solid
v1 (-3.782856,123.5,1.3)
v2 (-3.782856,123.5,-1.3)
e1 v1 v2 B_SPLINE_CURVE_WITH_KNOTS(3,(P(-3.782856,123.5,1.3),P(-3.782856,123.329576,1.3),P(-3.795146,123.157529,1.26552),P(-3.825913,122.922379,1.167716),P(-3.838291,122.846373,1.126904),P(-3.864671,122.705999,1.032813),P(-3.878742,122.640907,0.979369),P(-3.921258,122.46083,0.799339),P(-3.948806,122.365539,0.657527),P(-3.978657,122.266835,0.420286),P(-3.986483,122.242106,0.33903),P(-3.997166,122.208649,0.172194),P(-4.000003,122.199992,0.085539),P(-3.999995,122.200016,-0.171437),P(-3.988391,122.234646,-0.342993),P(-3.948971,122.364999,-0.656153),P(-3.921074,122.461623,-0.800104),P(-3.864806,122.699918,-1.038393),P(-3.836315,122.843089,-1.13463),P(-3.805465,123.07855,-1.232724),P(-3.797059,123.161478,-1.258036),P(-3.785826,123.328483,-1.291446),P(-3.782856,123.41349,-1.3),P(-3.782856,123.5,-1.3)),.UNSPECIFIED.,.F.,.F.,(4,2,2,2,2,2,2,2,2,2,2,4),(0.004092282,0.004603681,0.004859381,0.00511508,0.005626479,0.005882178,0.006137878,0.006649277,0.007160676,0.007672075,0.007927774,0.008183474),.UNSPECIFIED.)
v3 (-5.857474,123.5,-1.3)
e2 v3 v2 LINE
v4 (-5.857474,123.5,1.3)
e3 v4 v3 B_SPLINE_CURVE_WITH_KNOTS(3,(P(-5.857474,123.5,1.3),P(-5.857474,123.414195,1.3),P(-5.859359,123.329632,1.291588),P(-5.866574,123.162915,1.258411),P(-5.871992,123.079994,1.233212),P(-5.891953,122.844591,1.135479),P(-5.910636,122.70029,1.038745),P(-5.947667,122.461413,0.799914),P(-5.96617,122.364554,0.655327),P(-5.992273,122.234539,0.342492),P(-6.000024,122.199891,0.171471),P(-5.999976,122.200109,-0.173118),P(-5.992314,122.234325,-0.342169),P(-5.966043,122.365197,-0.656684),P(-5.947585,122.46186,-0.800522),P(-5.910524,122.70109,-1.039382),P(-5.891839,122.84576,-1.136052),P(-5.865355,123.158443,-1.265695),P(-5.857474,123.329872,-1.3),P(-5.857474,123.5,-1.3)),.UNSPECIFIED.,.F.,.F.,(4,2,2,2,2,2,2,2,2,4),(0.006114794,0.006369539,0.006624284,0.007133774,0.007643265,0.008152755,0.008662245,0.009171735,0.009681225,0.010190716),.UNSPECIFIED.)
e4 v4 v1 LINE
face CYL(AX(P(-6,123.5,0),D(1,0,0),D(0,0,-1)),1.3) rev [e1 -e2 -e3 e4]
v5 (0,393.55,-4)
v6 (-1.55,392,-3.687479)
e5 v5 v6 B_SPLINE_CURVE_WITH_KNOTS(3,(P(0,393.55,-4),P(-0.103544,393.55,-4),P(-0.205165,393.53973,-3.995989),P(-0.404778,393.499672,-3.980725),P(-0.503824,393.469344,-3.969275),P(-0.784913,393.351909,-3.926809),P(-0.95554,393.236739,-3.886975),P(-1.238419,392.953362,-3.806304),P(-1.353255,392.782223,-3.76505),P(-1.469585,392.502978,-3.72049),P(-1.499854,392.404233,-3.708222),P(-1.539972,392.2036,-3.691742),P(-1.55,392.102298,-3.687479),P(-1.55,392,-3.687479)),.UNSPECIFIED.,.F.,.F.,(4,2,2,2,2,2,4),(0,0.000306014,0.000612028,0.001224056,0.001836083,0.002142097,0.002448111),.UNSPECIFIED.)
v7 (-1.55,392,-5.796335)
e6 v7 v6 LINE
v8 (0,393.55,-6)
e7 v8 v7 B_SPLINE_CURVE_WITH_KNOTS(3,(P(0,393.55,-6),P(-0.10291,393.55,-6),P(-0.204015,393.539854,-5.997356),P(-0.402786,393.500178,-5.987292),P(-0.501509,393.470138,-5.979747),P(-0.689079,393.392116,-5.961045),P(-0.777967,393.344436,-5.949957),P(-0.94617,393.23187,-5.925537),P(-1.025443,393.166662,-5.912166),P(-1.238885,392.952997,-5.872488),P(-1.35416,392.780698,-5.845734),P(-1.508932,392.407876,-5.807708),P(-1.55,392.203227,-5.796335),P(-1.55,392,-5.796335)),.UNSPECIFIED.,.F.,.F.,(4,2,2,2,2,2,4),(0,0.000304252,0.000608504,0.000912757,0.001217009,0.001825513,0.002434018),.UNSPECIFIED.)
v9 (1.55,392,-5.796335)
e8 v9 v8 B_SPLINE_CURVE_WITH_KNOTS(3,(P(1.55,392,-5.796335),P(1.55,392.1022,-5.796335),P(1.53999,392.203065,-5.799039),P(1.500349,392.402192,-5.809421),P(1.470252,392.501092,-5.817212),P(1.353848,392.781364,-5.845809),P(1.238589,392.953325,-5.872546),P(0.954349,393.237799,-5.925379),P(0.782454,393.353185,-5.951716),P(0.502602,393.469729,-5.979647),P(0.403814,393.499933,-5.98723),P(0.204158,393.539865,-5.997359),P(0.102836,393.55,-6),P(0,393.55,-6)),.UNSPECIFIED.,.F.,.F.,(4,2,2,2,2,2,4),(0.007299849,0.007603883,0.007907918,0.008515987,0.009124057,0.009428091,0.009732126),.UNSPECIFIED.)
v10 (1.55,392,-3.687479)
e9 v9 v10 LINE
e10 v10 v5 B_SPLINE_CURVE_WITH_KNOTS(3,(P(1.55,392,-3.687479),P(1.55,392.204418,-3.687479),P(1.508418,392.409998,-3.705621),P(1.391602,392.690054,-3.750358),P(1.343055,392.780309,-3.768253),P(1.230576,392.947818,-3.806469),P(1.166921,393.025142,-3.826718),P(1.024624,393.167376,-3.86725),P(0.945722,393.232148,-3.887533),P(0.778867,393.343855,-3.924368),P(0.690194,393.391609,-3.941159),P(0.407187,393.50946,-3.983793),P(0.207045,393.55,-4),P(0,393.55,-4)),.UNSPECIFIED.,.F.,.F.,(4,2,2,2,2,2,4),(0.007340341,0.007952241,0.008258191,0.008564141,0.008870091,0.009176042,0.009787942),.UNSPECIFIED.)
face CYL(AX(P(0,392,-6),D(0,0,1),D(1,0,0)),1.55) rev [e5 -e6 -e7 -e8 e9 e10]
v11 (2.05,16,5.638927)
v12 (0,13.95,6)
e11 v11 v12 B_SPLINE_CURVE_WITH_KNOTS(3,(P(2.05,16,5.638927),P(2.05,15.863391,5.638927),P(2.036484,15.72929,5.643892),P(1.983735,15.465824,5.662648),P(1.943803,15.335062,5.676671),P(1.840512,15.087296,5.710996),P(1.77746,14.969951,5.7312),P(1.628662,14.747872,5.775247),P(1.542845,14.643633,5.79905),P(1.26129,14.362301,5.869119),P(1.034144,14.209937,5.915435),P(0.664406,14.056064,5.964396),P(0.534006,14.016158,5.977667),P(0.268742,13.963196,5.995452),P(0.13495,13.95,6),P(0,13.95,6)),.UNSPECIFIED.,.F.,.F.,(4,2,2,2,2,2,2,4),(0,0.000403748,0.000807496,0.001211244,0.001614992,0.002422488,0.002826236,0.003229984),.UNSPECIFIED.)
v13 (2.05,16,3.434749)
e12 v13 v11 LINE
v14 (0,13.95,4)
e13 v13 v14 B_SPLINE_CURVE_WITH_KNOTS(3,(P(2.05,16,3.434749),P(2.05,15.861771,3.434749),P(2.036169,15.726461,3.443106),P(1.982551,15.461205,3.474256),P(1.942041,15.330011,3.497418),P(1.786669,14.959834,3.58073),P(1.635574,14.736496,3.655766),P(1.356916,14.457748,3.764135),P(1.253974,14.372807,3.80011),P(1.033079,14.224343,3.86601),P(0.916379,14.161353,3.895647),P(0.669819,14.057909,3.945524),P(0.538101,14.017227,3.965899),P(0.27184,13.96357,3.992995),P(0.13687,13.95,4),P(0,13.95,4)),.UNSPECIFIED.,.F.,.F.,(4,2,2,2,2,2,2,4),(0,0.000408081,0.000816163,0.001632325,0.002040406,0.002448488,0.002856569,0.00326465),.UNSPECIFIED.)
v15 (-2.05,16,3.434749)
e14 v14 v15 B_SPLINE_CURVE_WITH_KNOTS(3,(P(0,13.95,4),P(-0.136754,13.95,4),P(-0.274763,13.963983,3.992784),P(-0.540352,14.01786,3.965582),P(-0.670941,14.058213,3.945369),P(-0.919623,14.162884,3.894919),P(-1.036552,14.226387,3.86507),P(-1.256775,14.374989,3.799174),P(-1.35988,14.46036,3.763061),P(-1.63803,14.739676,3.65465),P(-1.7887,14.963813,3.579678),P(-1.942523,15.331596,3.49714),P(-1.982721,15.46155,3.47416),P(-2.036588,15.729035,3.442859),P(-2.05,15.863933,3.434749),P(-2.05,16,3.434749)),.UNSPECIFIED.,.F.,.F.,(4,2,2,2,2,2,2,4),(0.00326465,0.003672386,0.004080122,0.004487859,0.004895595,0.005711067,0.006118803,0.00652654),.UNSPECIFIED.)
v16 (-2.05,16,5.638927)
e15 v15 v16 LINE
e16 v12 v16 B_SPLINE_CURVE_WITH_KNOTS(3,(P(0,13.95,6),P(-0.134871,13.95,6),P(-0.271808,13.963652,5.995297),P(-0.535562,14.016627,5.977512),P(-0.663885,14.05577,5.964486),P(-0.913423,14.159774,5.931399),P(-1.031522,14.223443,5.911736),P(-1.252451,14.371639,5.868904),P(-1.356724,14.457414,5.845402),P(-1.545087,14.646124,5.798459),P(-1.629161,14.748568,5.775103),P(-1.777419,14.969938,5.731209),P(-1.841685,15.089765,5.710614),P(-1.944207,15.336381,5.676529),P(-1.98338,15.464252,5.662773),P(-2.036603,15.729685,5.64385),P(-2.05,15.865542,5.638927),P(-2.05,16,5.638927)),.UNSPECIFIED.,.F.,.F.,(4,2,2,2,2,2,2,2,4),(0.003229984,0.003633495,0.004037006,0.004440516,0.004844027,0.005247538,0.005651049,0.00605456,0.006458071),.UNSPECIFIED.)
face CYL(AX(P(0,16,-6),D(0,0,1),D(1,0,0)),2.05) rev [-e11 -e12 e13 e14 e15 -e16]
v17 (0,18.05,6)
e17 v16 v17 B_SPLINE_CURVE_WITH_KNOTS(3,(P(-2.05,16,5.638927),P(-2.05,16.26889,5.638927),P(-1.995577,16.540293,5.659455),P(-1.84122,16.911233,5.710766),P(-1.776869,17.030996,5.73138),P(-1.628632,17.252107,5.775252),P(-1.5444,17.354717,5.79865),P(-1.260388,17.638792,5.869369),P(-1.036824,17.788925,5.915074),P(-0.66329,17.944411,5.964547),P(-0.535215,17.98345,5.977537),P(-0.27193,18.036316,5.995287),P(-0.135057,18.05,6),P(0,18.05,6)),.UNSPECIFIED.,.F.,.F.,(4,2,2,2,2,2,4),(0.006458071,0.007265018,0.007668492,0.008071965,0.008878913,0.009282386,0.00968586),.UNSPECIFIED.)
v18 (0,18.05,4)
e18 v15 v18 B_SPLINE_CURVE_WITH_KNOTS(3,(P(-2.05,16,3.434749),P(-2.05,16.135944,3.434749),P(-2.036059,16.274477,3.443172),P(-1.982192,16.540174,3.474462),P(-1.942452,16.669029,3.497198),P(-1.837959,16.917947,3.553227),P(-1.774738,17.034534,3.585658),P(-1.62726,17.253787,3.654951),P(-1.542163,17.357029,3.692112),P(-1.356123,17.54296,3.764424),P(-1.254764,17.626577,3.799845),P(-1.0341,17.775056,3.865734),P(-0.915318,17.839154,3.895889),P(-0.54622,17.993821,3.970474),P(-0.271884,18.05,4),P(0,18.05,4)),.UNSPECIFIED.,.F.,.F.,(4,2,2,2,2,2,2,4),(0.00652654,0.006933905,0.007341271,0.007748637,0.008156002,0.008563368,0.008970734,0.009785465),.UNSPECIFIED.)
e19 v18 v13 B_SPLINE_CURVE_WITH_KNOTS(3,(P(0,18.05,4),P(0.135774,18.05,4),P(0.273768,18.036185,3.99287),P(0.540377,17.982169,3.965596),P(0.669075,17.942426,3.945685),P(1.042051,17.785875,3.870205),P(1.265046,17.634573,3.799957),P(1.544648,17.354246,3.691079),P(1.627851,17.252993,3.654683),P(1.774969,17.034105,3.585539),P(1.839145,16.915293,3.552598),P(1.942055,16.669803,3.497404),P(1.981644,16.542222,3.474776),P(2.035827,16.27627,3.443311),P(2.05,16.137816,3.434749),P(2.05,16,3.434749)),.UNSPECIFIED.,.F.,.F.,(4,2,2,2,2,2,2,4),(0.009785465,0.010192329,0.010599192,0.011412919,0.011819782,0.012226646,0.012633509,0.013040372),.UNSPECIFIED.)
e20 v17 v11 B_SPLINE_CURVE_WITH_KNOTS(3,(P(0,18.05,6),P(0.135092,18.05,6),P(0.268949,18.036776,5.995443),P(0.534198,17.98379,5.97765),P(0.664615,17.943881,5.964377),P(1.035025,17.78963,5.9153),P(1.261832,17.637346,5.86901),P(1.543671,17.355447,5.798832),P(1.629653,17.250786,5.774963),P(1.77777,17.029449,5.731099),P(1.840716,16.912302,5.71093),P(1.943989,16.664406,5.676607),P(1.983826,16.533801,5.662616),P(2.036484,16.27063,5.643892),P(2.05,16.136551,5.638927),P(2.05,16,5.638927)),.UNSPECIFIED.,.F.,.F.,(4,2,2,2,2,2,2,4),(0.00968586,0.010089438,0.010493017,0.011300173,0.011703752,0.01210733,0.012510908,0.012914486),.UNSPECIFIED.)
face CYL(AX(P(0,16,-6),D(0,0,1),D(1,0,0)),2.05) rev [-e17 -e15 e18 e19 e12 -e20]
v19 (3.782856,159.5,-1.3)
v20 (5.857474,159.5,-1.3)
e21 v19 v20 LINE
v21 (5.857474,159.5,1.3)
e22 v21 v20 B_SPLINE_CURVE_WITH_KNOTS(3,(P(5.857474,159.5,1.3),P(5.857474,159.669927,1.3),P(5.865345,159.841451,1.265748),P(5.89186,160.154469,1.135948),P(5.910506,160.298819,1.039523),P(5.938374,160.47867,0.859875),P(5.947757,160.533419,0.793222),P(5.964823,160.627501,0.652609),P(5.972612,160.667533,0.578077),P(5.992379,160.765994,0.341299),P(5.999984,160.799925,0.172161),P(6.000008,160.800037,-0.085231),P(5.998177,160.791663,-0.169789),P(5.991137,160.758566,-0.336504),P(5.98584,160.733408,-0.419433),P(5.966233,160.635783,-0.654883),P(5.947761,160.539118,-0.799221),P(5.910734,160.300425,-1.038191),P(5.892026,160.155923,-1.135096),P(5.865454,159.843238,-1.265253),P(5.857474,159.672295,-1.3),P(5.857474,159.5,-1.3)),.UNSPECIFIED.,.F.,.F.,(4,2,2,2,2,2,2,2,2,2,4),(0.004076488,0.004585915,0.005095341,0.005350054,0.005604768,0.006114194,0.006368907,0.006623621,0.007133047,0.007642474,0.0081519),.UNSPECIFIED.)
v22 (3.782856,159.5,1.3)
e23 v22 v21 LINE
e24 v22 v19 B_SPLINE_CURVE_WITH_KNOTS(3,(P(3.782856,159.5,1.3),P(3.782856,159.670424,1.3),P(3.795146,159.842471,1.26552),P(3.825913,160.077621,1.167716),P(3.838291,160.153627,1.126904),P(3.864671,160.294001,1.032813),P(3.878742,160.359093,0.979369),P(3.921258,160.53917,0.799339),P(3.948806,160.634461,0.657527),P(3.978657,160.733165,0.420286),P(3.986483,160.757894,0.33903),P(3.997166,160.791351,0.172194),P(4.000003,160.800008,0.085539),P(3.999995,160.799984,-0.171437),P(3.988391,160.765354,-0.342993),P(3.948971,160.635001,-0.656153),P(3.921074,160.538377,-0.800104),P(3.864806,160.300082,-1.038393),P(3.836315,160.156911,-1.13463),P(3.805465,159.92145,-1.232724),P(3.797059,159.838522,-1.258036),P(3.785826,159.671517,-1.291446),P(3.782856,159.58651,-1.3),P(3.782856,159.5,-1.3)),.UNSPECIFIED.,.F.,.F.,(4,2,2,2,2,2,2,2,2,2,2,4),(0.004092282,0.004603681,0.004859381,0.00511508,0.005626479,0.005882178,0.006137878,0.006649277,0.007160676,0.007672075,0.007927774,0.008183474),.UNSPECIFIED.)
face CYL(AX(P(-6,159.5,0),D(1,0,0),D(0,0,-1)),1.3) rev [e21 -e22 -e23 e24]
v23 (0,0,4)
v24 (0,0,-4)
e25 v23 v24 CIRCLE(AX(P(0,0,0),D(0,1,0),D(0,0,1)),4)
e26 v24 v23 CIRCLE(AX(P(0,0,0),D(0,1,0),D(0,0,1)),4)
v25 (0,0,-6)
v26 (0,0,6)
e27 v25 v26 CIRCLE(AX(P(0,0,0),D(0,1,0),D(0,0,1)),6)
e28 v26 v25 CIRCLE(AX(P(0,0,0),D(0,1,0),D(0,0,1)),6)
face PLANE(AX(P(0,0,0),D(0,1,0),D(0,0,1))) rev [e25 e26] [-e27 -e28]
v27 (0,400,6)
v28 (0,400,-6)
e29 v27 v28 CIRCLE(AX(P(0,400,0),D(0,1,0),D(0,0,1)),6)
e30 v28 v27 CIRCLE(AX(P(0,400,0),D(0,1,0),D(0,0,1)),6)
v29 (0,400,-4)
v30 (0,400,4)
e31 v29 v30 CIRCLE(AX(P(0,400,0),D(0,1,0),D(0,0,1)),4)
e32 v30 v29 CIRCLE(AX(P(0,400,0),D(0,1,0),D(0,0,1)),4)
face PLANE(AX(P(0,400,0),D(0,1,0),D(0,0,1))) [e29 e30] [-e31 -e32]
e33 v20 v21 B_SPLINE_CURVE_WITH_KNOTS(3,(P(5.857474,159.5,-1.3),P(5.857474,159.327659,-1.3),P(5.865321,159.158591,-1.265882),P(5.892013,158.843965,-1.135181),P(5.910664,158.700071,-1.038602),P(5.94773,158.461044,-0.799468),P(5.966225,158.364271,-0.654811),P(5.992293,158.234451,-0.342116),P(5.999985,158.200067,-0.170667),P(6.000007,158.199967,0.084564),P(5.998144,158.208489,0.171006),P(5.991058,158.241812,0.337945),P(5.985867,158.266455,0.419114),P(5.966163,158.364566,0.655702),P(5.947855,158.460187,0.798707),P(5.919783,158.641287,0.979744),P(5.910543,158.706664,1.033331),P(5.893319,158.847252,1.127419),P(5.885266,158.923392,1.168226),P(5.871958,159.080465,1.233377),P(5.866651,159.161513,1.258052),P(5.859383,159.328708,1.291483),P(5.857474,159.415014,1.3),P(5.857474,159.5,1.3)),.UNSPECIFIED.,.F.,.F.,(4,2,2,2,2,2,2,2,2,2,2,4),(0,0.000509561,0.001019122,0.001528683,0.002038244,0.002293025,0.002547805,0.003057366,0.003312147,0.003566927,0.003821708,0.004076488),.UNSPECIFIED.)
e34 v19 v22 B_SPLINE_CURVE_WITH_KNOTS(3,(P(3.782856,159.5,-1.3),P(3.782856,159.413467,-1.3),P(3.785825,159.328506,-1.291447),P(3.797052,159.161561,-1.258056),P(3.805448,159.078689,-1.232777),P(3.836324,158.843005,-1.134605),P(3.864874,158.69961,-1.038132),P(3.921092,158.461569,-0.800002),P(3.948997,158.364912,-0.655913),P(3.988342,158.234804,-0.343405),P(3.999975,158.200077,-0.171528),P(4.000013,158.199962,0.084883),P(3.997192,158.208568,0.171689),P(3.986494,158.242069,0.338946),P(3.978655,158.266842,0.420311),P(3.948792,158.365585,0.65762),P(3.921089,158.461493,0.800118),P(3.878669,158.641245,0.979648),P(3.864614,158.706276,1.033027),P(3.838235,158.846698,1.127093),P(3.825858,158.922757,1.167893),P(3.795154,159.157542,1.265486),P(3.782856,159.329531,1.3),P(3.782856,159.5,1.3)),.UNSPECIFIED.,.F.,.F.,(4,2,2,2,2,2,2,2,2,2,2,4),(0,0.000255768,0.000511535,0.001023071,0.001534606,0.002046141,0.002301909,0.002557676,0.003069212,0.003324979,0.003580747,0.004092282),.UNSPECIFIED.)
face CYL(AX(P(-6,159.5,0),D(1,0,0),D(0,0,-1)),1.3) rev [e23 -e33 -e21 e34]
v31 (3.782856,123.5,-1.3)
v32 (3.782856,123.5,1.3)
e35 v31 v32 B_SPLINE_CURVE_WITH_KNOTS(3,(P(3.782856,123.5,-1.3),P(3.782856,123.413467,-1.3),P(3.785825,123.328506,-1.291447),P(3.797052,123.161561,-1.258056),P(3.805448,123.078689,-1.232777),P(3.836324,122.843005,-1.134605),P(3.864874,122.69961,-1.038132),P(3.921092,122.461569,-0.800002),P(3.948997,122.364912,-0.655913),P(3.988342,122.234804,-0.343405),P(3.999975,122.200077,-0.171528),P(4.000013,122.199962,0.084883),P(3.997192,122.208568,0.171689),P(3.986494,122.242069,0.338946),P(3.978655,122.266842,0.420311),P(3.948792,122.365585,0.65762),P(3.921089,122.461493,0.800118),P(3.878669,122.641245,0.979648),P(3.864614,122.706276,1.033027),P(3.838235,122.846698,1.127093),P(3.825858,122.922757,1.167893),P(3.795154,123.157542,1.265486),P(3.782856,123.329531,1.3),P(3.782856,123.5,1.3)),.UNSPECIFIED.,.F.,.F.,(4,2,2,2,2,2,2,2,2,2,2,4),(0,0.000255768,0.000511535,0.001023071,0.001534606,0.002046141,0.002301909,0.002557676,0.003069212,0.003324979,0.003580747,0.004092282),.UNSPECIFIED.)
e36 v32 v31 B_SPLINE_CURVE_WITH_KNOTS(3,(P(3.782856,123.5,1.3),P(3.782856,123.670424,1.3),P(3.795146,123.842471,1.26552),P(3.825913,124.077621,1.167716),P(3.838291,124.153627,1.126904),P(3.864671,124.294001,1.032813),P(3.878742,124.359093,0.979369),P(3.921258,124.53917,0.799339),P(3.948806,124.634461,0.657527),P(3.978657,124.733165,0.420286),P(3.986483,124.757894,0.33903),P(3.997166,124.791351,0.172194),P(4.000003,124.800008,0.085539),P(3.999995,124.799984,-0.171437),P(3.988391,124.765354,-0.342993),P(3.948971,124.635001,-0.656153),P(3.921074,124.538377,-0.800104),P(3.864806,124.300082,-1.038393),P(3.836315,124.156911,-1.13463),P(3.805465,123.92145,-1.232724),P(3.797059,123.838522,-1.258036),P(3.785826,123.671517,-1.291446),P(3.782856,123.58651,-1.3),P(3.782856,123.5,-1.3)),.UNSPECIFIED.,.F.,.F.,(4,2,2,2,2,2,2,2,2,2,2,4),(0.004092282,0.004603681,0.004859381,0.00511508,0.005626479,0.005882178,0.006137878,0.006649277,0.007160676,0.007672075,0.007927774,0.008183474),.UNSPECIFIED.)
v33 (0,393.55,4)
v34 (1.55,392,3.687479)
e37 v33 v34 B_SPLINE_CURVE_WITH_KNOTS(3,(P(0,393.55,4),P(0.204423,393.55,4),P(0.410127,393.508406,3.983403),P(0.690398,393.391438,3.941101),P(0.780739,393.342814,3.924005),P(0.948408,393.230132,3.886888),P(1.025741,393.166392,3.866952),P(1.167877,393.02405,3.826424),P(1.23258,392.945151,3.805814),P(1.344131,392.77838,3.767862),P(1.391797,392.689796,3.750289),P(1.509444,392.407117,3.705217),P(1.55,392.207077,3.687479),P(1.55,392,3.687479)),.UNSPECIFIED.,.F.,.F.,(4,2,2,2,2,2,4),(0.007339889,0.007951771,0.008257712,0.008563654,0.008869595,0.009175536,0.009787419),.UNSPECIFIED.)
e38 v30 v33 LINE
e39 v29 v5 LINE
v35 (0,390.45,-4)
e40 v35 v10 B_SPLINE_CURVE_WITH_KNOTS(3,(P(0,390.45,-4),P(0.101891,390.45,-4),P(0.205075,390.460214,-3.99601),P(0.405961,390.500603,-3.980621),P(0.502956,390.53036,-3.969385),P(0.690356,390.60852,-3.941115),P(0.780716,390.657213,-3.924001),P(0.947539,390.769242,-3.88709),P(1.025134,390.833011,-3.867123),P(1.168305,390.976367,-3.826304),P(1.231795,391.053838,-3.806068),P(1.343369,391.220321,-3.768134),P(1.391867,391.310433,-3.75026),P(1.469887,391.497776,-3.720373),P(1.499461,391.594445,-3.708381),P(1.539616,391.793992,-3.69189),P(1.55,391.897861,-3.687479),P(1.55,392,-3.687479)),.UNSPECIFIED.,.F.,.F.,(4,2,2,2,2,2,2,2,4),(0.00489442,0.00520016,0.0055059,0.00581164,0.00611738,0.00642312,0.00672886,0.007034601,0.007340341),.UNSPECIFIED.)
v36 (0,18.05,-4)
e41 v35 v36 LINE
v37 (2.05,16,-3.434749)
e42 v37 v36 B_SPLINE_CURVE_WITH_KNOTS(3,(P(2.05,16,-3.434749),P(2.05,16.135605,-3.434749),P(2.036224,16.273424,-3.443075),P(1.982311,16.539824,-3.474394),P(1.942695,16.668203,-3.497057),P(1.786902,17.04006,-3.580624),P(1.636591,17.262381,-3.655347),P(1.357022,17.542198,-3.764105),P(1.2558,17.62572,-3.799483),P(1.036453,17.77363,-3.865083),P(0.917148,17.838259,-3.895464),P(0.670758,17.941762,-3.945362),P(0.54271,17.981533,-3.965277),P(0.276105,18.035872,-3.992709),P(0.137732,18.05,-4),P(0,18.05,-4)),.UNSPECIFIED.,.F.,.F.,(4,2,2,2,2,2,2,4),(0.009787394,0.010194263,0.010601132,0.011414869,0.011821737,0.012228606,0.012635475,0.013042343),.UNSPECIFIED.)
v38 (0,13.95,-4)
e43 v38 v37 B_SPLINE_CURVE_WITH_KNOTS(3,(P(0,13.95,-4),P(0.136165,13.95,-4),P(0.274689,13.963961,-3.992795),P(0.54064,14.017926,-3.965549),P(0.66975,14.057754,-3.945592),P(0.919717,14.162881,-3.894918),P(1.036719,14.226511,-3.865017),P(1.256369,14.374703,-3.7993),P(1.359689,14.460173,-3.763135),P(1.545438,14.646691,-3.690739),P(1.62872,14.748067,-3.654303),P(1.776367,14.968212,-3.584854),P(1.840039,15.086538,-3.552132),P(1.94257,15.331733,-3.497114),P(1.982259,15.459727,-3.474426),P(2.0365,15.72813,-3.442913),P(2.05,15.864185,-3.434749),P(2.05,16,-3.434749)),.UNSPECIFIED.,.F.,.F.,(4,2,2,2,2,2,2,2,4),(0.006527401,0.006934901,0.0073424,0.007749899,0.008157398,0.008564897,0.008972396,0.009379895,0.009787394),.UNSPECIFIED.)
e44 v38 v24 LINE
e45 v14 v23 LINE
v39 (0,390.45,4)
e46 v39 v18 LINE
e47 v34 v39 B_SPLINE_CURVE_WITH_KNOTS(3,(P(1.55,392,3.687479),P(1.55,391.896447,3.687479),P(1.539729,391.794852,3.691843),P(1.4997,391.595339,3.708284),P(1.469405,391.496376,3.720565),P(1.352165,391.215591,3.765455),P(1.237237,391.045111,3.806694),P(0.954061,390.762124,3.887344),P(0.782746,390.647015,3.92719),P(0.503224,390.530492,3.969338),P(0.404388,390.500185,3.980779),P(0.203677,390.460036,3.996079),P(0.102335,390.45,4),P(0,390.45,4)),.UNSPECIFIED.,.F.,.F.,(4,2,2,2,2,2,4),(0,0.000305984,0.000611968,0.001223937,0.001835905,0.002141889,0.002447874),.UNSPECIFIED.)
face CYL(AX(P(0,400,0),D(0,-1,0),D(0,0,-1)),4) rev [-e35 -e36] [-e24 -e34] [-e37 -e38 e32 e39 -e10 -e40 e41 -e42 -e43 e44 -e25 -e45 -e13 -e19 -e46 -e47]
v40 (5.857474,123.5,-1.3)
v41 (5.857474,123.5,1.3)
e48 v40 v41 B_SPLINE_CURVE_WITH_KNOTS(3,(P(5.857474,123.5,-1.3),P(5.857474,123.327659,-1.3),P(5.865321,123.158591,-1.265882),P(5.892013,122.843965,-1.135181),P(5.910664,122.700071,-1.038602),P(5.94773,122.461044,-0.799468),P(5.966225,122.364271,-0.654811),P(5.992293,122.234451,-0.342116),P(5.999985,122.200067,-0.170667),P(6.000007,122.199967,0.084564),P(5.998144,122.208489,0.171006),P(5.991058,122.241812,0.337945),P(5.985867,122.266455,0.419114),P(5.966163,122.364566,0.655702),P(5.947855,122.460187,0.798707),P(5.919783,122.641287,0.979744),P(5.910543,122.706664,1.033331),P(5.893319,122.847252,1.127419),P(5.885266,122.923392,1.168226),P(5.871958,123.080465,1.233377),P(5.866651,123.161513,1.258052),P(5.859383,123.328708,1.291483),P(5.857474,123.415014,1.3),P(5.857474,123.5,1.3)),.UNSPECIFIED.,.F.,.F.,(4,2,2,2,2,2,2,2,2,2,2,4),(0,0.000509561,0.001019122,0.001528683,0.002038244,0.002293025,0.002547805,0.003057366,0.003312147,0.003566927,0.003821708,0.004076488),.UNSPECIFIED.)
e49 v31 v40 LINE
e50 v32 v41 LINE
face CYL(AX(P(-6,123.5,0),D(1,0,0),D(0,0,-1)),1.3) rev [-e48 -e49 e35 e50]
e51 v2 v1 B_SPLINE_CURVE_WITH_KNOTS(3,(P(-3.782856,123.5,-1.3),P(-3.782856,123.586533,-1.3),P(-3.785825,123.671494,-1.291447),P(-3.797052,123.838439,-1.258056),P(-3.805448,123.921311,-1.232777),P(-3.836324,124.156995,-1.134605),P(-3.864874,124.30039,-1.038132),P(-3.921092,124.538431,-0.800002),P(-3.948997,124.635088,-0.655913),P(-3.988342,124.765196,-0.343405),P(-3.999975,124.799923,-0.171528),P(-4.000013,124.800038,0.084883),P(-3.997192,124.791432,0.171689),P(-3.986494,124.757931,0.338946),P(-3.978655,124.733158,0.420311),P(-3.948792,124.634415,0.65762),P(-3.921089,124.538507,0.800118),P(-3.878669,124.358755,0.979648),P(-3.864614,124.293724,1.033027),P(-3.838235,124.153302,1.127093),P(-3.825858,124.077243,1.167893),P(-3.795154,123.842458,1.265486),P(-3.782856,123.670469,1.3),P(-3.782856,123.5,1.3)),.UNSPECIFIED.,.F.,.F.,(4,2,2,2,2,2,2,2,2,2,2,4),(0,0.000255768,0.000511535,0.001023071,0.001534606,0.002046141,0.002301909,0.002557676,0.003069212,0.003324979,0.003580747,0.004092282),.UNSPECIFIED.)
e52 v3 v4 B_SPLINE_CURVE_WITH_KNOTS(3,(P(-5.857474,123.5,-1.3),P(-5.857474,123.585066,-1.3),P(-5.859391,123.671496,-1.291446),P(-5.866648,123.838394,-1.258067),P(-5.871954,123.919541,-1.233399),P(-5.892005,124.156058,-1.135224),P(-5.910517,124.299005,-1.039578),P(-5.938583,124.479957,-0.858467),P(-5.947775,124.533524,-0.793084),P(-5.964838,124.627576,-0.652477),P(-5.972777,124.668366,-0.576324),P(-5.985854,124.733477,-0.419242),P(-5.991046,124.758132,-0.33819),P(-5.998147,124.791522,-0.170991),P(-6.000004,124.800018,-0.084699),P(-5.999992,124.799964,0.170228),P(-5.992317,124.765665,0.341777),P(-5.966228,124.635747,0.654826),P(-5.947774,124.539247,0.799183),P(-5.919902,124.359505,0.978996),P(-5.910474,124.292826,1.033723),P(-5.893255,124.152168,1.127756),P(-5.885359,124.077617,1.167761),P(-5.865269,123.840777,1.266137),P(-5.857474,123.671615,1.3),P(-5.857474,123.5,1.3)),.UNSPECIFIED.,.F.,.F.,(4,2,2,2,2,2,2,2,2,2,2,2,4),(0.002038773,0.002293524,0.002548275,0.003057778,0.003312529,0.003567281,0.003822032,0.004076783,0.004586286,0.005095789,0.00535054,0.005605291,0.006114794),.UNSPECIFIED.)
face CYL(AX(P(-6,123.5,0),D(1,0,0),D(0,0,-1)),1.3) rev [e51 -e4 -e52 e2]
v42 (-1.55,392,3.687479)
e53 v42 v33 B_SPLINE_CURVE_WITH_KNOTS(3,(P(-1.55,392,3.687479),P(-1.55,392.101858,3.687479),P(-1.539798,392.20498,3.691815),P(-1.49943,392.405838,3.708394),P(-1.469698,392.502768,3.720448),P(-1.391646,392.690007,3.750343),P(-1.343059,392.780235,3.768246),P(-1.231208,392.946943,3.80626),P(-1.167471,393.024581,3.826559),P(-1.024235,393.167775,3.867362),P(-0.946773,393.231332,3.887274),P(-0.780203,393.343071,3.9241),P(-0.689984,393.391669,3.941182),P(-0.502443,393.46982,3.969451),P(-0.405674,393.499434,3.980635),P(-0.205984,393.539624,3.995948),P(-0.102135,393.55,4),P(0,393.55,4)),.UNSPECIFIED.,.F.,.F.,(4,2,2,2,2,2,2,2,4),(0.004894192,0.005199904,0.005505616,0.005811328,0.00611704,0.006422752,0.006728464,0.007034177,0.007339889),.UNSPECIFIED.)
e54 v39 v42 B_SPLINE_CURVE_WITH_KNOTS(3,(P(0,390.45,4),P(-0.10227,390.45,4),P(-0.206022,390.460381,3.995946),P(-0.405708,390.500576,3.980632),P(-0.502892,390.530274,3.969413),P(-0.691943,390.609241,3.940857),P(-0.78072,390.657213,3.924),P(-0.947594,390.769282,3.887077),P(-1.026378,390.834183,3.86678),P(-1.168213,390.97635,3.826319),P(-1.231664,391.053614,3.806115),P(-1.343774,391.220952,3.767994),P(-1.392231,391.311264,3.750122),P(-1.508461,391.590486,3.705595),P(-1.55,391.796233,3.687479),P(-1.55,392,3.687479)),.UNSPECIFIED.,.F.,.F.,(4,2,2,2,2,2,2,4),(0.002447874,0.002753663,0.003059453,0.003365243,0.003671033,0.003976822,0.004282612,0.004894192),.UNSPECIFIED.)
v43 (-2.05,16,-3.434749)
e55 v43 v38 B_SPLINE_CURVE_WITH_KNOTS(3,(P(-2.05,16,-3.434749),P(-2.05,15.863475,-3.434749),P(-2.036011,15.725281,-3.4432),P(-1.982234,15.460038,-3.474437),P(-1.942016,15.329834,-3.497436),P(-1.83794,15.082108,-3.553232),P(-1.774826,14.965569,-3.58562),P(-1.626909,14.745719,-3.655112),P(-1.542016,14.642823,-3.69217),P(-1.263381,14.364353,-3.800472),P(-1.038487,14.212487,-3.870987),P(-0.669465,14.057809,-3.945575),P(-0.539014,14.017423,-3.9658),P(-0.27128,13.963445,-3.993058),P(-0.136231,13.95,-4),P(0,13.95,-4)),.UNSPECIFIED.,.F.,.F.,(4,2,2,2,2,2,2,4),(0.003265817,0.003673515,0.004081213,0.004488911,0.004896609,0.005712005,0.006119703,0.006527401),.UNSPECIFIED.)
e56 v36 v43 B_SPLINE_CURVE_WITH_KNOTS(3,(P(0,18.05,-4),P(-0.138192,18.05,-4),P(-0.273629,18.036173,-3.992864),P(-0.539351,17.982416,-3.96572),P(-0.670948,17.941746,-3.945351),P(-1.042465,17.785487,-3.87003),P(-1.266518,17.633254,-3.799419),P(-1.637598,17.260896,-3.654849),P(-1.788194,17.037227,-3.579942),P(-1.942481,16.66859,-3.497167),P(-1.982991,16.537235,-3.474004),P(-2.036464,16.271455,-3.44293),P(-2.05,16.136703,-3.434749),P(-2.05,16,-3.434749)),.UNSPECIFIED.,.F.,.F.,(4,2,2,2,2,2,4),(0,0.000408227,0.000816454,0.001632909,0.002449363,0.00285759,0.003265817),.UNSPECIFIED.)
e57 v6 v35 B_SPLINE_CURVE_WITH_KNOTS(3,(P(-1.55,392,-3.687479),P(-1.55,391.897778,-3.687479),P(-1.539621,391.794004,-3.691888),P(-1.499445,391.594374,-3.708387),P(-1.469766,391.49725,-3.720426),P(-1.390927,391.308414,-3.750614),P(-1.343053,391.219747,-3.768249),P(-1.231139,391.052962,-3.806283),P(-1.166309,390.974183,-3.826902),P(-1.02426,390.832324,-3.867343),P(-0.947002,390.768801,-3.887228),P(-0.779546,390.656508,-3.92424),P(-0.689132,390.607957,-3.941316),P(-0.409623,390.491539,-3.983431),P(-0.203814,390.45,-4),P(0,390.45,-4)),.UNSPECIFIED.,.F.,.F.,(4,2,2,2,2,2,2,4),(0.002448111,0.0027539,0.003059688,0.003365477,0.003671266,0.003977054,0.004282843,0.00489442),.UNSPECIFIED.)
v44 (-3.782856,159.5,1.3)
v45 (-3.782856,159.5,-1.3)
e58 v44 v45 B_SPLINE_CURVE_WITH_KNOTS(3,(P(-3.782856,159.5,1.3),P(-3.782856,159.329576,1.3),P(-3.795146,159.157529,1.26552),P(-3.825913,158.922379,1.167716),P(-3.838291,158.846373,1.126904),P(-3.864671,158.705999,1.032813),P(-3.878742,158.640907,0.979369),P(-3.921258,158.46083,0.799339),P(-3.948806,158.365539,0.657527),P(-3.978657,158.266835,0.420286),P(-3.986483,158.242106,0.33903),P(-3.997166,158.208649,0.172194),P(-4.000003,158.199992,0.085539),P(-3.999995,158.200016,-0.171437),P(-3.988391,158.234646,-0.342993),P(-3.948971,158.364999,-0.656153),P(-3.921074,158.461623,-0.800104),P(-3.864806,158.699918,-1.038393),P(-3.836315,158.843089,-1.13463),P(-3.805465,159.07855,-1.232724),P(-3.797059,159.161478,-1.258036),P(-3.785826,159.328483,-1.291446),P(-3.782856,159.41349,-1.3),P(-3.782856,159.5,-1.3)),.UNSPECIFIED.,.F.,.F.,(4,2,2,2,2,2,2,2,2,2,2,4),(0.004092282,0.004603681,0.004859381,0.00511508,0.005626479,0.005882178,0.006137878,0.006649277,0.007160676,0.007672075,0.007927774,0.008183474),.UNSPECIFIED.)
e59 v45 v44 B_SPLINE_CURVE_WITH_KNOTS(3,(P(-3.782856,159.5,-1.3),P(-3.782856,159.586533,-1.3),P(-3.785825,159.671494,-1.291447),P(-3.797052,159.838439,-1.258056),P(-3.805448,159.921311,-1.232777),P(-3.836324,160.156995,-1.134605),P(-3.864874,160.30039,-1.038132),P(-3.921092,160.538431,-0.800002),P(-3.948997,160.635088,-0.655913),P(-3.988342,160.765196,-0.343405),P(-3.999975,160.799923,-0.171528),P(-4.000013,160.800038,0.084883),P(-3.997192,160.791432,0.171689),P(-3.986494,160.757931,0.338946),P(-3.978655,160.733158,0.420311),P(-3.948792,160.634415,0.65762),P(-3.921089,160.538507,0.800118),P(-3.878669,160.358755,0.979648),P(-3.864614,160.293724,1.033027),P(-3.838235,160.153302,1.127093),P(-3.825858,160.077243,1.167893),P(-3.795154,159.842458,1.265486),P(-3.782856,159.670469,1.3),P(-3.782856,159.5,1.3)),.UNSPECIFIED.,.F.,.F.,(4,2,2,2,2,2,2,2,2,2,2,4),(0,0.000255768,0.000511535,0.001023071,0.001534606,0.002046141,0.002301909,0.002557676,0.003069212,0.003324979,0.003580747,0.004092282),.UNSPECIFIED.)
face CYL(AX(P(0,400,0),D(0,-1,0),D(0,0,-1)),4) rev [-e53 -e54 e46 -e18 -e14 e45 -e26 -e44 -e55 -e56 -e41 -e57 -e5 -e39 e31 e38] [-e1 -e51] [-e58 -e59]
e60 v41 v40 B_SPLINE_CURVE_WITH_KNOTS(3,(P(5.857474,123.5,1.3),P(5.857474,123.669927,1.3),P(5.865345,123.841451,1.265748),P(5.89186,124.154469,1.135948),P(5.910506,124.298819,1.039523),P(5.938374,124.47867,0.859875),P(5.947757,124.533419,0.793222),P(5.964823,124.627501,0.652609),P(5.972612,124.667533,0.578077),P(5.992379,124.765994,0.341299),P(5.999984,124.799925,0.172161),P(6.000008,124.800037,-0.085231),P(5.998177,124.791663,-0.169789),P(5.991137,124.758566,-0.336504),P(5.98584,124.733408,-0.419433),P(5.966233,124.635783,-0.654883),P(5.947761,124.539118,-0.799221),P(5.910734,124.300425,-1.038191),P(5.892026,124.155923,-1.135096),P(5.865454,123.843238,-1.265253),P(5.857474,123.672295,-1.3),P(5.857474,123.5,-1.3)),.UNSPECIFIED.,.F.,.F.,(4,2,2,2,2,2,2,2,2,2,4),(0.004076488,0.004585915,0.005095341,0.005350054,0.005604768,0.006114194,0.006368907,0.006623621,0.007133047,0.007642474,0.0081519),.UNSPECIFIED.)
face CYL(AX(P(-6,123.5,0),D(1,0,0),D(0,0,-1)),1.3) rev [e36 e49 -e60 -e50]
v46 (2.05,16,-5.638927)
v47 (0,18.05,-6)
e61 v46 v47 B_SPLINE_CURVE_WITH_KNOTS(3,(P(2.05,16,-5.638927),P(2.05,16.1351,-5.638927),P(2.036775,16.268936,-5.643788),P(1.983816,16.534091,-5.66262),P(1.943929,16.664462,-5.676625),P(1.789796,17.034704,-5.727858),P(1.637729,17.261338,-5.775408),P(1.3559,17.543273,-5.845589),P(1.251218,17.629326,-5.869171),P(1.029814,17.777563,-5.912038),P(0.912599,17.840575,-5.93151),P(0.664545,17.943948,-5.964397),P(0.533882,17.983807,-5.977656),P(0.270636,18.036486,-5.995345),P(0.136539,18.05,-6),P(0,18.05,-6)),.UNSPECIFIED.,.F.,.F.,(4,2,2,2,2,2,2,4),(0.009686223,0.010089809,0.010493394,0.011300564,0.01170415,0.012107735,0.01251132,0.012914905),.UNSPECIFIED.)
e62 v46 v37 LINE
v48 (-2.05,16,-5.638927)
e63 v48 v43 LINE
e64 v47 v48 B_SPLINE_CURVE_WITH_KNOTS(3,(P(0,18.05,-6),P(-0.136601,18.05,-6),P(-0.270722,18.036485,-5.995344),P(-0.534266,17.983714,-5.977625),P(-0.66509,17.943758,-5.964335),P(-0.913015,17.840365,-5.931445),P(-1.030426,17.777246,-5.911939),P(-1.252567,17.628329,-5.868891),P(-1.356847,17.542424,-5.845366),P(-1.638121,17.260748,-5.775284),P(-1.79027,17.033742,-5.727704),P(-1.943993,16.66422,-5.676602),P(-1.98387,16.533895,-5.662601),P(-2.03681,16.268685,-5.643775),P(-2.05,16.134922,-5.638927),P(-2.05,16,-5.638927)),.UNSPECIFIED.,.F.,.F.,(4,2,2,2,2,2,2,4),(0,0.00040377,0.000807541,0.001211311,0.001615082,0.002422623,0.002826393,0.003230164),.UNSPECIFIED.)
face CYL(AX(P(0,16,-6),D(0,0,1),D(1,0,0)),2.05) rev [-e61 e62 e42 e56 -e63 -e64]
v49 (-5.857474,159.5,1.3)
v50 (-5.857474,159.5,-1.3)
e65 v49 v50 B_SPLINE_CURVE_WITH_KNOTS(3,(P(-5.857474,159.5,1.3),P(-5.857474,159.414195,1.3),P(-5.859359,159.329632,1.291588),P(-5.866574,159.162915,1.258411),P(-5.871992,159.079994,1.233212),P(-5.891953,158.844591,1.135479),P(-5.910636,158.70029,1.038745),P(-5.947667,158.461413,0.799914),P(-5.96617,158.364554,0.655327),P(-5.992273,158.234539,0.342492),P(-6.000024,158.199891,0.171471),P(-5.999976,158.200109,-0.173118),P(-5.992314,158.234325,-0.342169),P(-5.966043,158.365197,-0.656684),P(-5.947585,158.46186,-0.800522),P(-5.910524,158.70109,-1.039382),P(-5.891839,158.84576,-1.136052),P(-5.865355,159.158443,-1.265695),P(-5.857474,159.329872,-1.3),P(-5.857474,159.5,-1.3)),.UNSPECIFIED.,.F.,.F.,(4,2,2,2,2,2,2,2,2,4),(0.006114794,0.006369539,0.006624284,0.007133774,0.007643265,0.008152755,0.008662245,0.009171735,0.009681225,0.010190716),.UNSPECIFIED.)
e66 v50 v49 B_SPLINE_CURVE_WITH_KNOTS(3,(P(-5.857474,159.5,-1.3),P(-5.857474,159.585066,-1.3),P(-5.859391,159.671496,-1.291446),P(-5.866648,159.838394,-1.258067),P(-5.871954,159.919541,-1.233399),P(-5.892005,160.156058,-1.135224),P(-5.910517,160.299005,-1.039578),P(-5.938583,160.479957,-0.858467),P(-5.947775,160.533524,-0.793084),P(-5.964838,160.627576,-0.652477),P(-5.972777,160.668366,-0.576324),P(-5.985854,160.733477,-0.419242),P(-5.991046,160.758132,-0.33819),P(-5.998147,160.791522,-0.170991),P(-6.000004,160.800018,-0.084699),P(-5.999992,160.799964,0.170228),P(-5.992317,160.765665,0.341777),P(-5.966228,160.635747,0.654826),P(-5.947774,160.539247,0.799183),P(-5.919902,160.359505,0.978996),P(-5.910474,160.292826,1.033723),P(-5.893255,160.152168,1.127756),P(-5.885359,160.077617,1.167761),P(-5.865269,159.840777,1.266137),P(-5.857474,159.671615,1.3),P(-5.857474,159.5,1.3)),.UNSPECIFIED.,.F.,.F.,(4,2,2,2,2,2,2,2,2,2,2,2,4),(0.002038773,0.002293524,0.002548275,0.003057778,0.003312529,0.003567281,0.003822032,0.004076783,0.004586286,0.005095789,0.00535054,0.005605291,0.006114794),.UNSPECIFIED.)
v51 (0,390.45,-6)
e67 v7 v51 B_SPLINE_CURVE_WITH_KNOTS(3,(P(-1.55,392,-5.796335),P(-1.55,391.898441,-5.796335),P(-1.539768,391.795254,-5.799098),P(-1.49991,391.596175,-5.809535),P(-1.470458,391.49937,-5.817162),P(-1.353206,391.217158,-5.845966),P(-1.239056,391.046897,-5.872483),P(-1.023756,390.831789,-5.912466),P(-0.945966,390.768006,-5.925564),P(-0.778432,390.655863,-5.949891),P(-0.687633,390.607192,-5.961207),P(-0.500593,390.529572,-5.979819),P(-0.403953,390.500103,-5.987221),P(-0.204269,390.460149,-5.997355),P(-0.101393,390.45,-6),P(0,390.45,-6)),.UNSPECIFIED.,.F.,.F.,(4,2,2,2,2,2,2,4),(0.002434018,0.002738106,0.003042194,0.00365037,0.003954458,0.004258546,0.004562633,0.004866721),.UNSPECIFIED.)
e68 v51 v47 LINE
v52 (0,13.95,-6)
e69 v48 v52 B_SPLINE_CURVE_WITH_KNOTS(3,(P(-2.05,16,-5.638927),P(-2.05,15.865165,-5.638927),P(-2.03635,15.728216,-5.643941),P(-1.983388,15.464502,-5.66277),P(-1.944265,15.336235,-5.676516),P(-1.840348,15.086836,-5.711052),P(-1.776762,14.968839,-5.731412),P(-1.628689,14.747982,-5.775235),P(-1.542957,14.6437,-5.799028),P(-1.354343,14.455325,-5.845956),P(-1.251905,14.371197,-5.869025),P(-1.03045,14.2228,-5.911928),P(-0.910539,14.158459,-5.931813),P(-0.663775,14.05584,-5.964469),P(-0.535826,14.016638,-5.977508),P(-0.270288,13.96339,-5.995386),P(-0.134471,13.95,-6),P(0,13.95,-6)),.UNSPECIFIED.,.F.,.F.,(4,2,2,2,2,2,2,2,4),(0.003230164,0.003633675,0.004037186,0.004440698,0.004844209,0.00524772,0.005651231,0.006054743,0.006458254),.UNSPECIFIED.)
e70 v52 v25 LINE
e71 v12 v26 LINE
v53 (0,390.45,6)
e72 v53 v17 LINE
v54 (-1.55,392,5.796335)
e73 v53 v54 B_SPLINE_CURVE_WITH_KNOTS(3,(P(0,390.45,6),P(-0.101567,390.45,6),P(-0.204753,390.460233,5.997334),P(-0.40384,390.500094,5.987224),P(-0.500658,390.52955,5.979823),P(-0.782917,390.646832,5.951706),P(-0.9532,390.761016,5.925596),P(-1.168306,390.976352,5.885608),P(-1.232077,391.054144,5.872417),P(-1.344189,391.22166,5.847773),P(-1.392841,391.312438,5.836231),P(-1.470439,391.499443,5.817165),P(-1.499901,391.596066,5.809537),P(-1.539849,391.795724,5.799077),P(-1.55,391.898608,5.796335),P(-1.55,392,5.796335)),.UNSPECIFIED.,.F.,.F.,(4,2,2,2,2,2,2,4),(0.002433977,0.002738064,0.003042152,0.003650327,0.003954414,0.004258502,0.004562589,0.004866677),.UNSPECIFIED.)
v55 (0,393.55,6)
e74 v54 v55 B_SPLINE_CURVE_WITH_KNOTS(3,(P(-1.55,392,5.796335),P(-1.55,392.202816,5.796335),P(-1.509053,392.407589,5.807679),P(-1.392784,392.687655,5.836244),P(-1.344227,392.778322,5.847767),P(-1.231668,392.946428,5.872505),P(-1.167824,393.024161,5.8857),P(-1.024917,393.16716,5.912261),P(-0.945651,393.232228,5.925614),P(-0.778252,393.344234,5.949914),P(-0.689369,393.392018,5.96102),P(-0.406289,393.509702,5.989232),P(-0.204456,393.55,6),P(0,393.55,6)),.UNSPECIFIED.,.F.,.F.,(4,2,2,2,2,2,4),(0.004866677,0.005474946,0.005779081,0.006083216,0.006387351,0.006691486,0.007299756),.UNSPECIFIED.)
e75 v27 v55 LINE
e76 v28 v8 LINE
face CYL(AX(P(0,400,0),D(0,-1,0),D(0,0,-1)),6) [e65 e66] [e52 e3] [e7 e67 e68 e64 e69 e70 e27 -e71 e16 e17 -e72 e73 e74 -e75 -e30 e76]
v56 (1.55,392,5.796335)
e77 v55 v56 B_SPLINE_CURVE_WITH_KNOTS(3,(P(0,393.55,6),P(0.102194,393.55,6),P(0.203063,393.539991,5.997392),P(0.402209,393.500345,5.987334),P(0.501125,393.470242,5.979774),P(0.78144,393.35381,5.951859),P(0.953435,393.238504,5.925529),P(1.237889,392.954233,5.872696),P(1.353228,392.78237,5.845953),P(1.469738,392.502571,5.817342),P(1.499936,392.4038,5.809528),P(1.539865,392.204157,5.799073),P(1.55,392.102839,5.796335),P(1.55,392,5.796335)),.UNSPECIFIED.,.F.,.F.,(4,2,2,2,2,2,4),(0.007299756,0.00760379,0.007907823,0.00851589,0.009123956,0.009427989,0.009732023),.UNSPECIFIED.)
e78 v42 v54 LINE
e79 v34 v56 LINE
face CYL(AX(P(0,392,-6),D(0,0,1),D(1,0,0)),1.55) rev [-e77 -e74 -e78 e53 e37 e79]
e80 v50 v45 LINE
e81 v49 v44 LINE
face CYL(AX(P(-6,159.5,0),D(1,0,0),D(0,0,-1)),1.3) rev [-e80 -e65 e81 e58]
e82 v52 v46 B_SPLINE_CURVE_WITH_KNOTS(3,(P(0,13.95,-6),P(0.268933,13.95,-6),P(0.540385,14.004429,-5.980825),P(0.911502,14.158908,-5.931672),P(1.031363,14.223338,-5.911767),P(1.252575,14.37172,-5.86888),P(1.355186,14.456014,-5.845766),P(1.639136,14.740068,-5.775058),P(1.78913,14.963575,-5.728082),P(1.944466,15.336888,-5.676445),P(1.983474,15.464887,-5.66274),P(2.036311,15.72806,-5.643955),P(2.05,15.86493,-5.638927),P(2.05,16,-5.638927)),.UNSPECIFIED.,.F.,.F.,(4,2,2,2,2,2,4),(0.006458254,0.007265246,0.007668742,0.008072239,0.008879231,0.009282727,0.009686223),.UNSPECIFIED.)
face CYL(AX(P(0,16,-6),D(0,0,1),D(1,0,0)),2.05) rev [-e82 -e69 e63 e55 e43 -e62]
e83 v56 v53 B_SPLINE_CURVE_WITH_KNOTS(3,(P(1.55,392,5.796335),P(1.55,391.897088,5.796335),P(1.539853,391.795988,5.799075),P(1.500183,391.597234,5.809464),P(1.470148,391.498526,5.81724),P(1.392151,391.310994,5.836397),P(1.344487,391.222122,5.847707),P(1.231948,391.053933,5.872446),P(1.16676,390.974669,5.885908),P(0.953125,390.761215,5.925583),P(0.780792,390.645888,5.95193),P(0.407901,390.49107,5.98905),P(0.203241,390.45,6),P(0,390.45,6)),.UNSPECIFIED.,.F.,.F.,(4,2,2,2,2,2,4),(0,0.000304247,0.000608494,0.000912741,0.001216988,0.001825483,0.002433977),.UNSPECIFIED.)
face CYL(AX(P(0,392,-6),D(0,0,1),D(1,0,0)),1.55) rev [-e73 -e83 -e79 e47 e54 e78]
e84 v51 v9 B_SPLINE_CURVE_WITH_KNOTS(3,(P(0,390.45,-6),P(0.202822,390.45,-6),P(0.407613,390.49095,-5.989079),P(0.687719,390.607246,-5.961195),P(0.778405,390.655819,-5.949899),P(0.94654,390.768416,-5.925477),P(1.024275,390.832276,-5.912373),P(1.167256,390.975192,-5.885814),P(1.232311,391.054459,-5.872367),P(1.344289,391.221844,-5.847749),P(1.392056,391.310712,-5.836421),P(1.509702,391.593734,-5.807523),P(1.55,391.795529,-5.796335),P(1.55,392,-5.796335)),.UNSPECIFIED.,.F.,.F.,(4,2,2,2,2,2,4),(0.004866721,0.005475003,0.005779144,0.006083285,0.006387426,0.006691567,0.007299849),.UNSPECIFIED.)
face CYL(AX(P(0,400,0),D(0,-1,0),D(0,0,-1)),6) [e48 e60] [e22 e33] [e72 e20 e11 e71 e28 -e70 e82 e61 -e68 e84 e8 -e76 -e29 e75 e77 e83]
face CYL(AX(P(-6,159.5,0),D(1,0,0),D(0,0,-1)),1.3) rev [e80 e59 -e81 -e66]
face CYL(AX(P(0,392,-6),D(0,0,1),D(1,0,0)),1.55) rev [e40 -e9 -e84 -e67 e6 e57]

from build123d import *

# Parameters (mm, degrees)
SKETCH_1_R               = 6
SKETCH_1_R_2             = 4
EXTRUDE_1_DEPTH          = 400
CUT_EXTRUDE_1_DEPTH      = 401.089989877
CUT_EXTRUDE_1_DEPTH_BACK = 401.089989877
SKETCH_2_R               = 2.05
SKETCH_2_R_2             = 1.55
CUT_EXTRUDE_2_DEPTH      = 401.089989981
CUT_EXTRUDE_2_DEPTH_BACK = 401.089989981
SKETCH_3_R               = 1.3


with BuildPart() as part:
    # 草图1 → 凸台-拉伸1 (new body)
    with BuildSketch(Plane(origin=(0, 0, 0), x_dir=(1, 0, 0), z_dir=(0, 1, 0))):
        with Locations(Location((0, 0, 0), (0, 0, 270))):
            Circle(SKETCH_1_R)
        with Locations(Location((0, 0, 0), (0, 0, 270))):
            Circle(SKETCH_1_R_2, mode=Mode.SUBTRACT)
    extrude(amount=EXTRUDE_1_DEPTH)

    # 草图2 → 切除-拉伸1 (cut, two sides: drawn at the far end of the back side and taken through both)
    with BuildSketch(Plane.XY.offset(-CUT_EXTRUDE_1_DEPTH_BACK)):
        with Locations((0, 16)):
            Circle(SKETCH_2_R)
        with Locations((0, 392)):
            Circle(SKETCH_2_R_2)
    extrude(amount=CUT_EXTRUDE_1_DEPTH + CUT_EXTRUDE_1_DEPTH_BACK, mode=Mode.SUBTRACT)

    # 草图3 → 切除-拉伸2 (cut, two sides: drawn at the far end of the back side and taken through both)
    with BuildSketch(Plane(origin=(0, 0, 0), x_dir=(0, 0, -1), z_dir=(1, 0, 0)).offset(-CUT_EXTRUDE_2_DEPTH_BACK)):
        with Locations((0, 159.5)):
            Circle(SKETCH_3_R)
        with Locations((0, 123.5)):
            Circle(SKETCH_3_R)
    extrude(amount=CUT_EXTRUDE_2_DEPTH + CUT_EXTRUDE_2_DEPTH_BACK, mode=Mode.SUBTRACT)


solid = part.part
